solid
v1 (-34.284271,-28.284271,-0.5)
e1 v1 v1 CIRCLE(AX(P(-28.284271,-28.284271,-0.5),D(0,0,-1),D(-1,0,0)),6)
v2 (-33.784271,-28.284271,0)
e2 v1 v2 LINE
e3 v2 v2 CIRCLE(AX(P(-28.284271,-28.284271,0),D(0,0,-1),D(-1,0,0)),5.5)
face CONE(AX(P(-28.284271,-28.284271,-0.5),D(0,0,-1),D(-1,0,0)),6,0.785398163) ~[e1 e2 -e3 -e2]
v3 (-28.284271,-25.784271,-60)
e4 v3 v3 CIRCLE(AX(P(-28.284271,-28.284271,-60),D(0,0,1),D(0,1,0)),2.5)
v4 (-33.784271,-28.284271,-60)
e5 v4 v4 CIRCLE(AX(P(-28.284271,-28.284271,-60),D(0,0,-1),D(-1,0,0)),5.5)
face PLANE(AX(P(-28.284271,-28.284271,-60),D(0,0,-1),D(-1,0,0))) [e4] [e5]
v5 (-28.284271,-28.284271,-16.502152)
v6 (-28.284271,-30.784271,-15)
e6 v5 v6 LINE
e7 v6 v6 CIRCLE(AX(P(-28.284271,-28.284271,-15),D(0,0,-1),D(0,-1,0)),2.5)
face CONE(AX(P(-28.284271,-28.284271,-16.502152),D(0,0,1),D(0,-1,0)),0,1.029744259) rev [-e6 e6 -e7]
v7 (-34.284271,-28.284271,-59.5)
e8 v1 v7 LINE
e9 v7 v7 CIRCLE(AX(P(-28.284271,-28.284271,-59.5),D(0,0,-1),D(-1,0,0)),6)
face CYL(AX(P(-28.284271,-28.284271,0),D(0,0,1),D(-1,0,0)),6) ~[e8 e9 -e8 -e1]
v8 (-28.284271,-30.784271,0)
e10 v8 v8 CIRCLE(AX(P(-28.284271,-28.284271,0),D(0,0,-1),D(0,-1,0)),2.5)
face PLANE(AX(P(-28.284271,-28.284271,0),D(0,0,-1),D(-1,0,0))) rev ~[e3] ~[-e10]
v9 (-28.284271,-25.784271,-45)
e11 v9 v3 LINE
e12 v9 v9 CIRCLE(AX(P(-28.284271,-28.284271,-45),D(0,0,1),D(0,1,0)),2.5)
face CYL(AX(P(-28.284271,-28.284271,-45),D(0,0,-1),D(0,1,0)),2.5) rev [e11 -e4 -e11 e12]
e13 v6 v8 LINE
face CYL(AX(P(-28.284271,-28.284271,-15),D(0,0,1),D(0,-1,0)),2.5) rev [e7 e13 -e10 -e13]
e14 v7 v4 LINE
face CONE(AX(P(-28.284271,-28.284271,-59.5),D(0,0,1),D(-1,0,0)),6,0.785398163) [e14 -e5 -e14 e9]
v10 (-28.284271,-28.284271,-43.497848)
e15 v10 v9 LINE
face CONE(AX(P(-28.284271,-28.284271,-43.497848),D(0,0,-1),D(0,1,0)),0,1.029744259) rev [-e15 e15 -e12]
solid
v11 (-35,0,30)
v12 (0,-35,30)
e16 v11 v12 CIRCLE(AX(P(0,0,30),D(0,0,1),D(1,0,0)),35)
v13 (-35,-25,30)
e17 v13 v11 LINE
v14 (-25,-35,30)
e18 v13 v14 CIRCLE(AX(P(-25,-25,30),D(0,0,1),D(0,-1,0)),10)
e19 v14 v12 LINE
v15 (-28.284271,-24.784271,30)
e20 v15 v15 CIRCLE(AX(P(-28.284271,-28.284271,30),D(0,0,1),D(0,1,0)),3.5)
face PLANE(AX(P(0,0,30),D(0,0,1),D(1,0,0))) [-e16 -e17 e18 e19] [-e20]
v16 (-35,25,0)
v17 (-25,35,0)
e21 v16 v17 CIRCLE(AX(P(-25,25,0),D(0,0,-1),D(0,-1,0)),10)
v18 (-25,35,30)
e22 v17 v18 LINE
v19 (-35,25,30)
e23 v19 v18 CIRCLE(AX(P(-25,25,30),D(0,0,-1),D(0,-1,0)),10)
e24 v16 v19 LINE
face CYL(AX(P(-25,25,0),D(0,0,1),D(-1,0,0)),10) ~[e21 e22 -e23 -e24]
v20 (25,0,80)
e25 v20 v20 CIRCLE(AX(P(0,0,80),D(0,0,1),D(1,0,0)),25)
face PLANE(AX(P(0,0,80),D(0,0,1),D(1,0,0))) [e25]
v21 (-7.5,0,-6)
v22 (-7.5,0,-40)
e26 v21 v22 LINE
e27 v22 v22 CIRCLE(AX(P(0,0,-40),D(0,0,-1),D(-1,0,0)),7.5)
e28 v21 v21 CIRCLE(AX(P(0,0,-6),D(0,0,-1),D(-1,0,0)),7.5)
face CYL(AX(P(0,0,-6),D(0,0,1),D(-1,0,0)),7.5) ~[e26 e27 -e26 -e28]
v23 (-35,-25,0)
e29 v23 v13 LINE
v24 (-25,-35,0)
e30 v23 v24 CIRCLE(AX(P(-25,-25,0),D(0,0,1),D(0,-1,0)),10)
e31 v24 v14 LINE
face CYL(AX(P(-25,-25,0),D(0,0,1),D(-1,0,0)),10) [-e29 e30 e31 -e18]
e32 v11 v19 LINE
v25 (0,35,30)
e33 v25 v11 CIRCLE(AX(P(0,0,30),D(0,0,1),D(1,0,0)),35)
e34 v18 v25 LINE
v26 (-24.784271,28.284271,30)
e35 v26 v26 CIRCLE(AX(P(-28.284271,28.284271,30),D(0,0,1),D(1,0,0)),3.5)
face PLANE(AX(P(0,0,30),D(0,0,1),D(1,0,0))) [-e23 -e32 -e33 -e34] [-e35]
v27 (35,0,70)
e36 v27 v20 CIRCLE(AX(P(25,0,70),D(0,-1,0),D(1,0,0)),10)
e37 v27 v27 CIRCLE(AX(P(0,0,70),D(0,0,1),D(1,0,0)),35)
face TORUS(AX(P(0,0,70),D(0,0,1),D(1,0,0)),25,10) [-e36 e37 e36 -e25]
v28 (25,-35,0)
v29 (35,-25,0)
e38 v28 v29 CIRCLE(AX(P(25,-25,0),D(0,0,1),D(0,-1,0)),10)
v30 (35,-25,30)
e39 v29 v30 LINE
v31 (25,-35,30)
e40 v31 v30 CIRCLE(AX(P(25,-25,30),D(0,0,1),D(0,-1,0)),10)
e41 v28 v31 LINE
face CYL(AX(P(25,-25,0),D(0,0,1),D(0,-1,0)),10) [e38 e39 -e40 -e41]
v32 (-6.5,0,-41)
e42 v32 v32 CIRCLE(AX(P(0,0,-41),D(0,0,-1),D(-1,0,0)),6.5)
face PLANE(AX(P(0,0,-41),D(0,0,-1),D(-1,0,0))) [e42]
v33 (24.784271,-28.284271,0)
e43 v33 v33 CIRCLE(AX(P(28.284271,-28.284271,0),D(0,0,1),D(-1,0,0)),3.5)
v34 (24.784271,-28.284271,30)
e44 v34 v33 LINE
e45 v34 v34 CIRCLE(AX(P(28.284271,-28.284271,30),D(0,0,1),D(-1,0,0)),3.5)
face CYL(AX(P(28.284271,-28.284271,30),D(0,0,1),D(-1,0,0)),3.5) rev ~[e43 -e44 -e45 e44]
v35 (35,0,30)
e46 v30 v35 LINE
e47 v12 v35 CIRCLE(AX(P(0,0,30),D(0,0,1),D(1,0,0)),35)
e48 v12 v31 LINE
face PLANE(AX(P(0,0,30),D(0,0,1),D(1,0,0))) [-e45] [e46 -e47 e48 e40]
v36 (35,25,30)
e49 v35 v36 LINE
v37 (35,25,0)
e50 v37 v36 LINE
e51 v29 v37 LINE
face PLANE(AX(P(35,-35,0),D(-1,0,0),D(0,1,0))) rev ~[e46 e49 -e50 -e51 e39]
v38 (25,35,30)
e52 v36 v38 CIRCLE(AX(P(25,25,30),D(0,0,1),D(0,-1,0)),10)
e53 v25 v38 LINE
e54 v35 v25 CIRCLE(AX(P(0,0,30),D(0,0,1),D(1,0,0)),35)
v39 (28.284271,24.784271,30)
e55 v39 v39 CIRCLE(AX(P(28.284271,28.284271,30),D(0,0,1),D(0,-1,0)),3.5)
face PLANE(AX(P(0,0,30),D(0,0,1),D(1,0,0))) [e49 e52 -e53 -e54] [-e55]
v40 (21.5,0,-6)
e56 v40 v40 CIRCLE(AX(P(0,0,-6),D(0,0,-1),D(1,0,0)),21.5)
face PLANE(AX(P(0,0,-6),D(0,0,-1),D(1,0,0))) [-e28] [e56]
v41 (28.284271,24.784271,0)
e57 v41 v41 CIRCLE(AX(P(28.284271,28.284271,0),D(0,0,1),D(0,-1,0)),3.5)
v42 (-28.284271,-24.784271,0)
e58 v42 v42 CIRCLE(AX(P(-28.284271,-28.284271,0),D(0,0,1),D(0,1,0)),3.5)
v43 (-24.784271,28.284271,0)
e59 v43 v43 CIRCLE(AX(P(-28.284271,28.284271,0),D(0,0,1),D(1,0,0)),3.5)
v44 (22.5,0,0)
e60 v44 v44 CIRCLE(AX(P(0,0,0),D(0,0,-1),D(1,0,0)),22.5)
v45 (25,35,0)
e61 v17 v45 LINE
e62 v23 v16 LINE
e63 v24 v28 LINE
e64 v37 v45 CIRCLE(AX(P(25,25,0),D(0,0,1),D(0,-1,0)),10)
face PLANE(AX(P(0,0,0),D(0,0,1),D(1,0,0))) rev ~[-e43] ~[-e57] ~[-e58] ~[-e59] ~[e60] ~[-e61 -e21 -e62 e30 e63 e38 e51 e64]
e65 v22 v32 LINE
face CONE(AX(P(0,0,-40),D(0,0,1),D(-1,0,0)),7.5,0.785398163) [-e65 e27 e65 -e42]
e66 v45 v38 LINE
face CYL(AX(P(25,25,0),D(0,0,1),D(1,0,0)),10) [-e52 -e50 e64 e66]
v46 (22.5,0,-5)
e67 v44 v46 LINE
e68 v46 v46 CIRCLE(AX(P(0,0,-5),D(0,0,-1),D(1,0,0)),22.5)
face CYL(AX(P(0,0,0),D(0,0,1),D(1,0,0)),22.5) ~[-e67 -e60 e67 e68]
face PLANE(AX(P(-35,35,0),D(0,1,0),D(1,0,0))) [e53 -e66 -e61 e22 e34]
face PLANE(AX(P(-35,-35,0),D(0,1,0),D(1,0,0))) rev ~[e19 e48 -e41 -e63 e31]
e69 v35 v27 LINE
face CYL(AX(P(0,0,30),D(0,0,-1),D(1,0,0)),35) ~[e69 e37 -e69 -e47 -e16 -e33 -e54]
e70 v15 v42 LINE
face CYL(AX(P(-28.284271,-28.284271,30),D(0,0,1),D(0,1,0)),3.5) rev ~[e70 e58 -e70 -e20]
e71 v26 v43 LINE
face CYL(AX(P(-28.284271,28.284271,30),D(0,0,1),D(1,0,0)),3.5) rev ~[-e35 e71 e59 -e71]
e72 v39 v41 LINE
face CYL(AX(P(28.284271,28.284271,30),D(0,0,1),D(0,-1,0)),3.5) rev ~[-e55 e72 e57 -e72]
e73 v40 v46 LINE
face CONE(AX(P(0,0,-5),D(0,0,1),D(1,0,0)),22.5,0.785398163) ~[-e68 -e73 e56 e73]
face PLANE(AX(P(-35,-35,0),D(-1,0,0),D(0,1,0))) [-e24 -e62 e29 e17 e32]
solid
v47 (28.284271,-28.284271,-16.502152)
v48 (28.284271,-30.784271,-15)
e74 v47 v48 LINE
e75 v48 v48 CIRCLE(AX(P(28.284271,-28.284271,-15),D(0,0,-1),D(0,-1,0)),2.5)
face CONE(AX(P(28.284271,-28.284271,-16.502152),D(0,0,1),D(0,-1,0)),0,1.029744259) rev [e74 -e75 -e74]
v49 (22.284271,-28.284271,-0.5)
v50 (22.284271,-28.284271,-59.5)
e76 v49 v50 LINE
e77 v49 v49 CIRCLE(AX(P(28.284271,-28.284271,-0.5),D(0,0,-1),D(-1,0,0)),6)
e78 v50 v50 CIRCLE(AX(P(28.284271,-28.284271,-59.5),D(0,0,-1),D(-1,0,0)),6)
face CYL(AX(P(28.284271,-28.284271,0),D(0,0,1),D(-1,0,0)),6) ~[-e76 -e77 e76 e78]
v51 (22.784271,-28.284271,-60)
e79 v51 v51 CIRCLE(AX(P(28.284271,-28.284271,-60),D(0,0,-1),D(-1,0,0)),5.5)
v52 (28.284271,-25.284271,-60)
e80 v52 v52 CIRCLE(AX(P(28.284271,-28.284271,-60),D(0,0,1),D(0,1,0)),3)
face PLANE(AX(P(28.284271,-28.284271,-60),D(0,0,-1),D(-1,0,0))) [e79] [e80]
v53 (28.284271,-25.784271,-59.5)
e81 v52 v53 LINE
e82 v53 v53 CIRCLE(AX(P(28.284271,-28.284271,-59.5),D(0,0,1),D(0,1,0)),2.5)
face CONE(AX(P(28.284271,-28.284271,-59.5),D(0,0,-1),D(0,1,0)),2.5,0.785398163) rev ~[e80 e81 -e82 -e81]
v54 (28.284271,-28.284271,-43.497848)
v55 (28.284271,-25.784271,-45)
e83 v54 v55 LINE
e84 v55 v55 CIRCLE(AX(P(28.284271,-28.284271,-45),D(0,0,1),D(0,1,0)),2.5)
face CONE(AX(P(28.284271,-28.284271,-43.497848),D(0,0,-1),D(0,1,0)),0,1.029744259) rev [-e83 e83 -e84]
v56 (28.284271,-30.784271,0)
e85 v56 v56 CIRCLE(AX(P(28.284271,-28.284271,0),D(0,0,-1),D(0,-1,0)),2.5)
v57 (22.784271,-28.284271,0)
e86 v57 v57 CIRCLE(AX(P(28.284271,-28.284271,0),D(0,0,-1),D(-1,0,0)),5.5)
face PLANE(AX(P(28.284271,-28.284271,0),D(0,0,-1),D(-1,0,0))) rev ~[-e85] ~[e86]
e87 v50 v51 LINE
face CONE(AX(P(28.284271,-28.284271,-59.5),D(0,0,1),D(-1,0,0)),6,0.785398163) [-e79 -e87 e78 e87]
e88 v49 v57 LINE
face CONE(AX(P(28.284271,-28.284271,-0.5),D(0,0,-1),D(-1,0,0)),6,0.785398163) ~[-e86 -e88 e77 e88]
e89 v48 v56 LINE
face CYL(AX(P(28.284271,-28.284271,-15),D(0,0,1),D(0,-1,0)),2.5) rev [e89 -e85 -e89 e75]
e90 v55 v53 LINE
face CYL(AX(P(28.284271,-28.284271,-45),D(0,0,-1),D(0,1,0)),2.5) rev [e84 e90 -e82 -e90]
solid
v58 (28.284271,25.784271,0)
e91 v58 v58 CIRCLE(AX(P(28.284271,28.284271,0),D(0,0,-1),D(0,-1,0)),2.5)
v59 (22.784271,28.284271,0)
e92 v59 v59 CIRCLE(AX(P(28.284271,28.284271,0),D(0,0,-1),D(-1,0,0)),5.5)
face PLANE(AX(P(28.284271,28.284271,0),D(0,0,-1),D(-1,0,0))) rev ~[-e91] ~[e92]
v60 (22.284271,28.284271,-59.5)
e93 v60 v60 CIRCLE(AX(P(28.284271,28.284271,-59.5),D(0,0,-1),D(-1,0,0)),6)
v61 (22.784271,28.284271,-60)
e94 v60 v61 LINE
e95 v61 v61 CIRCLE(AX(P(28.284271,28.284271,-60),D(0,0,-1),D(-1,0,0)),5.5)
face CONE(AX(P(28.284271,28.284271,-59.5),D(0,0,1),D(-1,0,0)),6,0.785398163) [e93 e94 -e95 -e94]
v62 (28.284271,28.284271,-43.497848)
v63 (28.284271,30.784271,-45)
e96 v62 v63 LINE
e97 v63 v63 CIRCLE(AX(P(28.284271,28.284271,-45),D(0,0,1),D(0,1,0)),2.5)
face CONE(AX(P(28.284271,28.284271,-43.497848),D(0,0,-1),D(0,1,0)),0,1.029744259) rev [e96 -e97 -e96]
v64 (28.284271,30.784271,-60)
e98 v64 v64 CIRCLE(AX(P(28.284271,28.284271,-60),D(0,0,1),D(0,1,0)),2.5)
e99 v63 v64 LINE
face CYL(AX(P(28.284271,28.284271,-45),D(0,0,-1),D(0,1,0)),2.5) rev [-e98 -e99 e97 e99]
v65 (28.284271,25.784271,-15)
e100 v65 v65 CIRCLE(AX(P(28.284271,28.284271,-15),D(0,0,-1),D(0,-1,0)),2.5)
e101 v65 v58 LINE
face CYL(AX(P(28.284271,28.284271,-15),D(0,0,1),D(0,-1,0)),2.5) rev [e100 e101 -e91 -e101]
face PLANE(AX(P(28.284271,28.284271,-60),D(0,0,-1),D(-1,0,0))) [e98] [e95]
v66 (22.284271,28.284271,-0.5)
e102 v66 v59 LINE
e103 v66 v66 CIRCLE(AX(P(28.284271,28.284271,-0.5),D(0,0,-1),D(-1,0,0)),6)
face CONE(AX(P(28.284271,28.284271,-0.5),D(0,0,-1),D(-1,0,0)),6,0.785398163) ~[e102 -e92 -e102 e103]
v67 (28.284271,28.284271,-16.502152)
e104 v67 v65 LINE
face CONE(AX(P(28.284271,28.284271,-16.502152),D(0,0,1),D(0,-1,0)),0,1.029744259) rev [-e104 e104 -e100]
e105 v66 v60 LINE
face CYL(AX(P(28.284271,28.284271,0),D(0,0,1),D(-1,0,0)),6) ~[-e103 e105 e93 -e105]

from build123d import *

# Parameters (mm, degrees)
SKETCH1_W                  = 70
SKETCH1_H                  = 70
BOSS_EXTRUDE1_DEPTH        = 30
FILLET2_R                  = 10
SKETCH3_R                  = 3.5
CUT_EXTRUDE1_DEPTH         = 60
SKETCH4_R                  = 22.5
BOSS_EXTRUDE3_DEPTH        = 6
SKETCH5_R                  = 7.5
BOSS_EXTRUDE4_DEPTH        = 35
CHAMFER1_SIZE              = 1
CHAMFER2_SIZE              = 1
CIRPATTERN1_COUNT          = 4
SKETCH6_R                  = 35
BOSS_EXTRUDE5_DEPTH        = 50
FILLET3_R                  = 10
SKETCH7_R                  = 6
BOSS_EXTRUDE6_DEPTH        = 60
BOSS_EXTRUDE6_2_DEPTH      = 60
BOSS_EXTRUDE6_3_DEPTH      = 60
M6_TAPPED_HOLE1_AT_2_COUNT = 2
M6_TAPPED_HOLE1_AT_2_PITCH = 80
M6_TAPPED_HOLE1_AT_3_COUNT = 2
M6_TAPPED_HOLE1_AT_3_PITCH = 56.568542495
CHAMFER3_SIZE              = 0.5
CHAMFER5_SIZE              = 0.5
CHAMFER6_SIZE              = 0.5
M6_TAPPED_HOLE2_AT_2_COUNT = 2
M6_TAPPED_HOLE2_AT_2_PITCH = 80
M6_TAPPED_HOLE2_AT_3_COUNT = 2
M6_TAPPED_HOLE2_AT_3_PITCH = 56.568542495


with BuildPart() as part:
    # Sketch1 → Boss-Extrude1 (new body)
    with BuildSketch(Plane.XY):
        Rectangle(SKETCH1_W, SKETCH1_H)
    extrude(amount=BOSS_EXTRUDE1_DEPTH)

    # Fillet2
    fillet2_edges = [part.edges().sort_by_distance(p)[0] for p in [
        (-35, 35, 15),
        (35, 35, 15),
        (35, -35, 15),
        (-35, -35, 15),
    ]]
    fillet(fillet2_edges, radius=FILLET2_R)

    # Sketch3 → Cut-Extrude1 (cut)
    with BuildSketch(Plane.XY.offset(30)):
        with Locations((-28.284271247, 28.284271247)):
            Circle(SKETCH3_R)
    cut_extrude1 = extrude(amount=-CUT_EXTRUDE1_DEPTH, mode=Mode.SUBTRACT)

    # Sketch4 → Boss-Extrude3 (add)
    with BuildSketch(Plane(origin=(0, 0, 0), x_dir=(-1, 0, 0), z_dir=(0, 0, -1))):
        with Locations(Location((0, 0, 0), (0, 0, 180))):
            Circle(SKETCH4_R)
    extrude(amount=BOSS_EXTRUDE3_DEPTH)

    # Sketch5 → Boss-Extrude4 (add)
    with BuildSketch(Plane(origin=(0, 0, -6), x_dir=(-1, 0, 0), z_dir=(0, 0, -1))):
        Circle(SKETCH5_R)
    extrude(amount=BOSS_EXTRUDE4_DEPTH)

    # Chamfer1
    chamfer1_edges = [part.edges().sort_by_distance(p)[0] for p in [
        (7.5, 0, -41),
    ]]
    chamfer(chamfer1_edges, length=CHAMFER1_SIZE)

    # Chamfer2
    chamfer2_edges = [part.edges().sort_by_distance(p)[0] for p in [
        (-22.5, 0, -6),
    ]]
    chamfer(chamfer2_edges, length=CHAMFER2_SIZE)

    # CirPattern1: Cut-Extrude1 ×4 about axis
    cirpattern1_axis = Axis((0, 0, 0), (0, 0, 1))
    for i in range(1, CIRPATTERN1_COUNT):
        add(cut_extrude1.rotate(cirpattern1_axis, i * 360 / CIRPATTERN1_COUNT), mode=Mode.SUBTRACT)

    # Sketch6 → Boss-Extrude5 (add)
    with BuildSketch(Plane.XY.offset(30)):
        Circle(SKETCH6_R)
    extrude(amount=BOSS_EXTRUDE5_DEPTH)

    # Fillet3
    fillet3_edges = [part.edges().sort_by_distance(p)[0] for p in [
        (-35, 0, 80),
    ]]
    fillet(fillet3_edges, radius=FILLET3_R)


with BuildPart() as body_2:
    # Sketch7 → Boss-Extrude6 (new body)
    with BuildSketch(Plane(origin=(0, 0, 0), x_dir=(-1, 0, 0), z_dir=(0, 0, -1))):
        with Locations((-28.284271247, 28.284271247)):
            Circle(SKETCH7_R)
    extrude(amount=BOSS_EXTRUDE6_DEPTH)

    # Sketch9 → M6 Tapped Hole1 (revolve, cut)
    with BuildSketch(Plane(origin=(28.284271247, 28.284271247, -60), x_dir=(0, 1, 0), z_dir=(1, 0, 0))):
        Polygon((0, 0), (0, 16.502151548), (2.5, 15), (2.5, 0), align=None)
    m6_tapped_hole1 = revolve(axis=Axis((28.284271247, 28.284271247, -66.35), (0, 0, 1)), mode=Mode.SUBTRACT)

    # Chamfer3
    chamfer3_edges = [body_2.edges().sort_by_distance(p)[0] for p in [
        (34.284271247, 28.284271247, 0),
        (34.284271247, 28.284271247, -60),
    ]]
    chamfer(chamfer3_edges, length=CHAMFER3_SIZE)

    # Sketch11 → M6 Tapped Hole2 (revolve, cut)
    with BuildSketch(Plane(origin=(28.284271247, 28.284271247, 0), x_dir=(0, -1, 0), z_dir=(1, 0, 0))):
        Polygon((0, 0), (0, 16.502151548), (2.5, 15), (2.5, 0), align=None)
    m6_tapped_hole2 = revolve(axis=Axis((28.284271247, 28.284271247, 6.35), (0, 0, -1)), mode=Mode.SUBTRACT)


with BuildPart() as body_3:
    # Sketch7 → Boss-Extrude6 2 (new body)
    with BuildSketch(Plane(origin=(0, 0, 0), x_dir=(-1, 0, 0), z_dir=(0, 0, -1))):
        with Locations((28.284271247, -28.284271247)):
            Circle(SKETCH7_R)
    extrude(amount=BOSS_EXTRUDE6_2_DEPTH)

    # M6 Tapped Hole1 at 2: M6 Tapped Hole1 ×2
    with Locations(*[Vector(-0.7071067811865429, -0.7071067811865522, 0) * (i * M6_TAPPED_HOLE1_AT_2_PITCH) for i in range(1, M6_TAPPED_HOLE1_AT_2_COUNT)]):
        add(m6_tapped_hole1, mode=Mode.SUBTRACT)

    # Chamfer6
    chamfer6_edges = [body_3.edges().sort_by_distance(p)[0] for p in [
        (-22.284271247, -28.284271247, 0),
        (-22.284271247, -28.284271247, -60),
    ]]
    chamfer(chamfer6_edges, length=CHAMFER6_SIZE)

    # M6 Tapped Hole2 at 2: M6 Tapped Hole2 ×2
    with Locations(*[Vector(-0.7071067811865429, -0.7071067811865522, 0) * (i * M6_TAPPED_HOLE2_AT_2_PITCH) for i in range(1, M6_TAPPED_HOLE2_AT_2_COUNT)]):
        add(m6_tapped_hole2, mode=Mode.SUBTRACT)


with BuildPart() as body_4:
    # Sketch7 → Boss-Extrude6 3 (new body)
    with BuildSketch(Plane(origin=(0, 0, 0), x_dir=(-1, 0, 0), z_dir=(0, 0, -1))):
        with Locations((-28.284271247, -28.284271247)):
            Circle(SKETCH7_R)
    extrude(amount=BOSS_EXTRUDE6_3_DEPTH)

    # M6 Tapped Hole1 at 3: M6 Tapped Hole1 ×2
    with Locations(*[(0, -i * M6_TAPPED_HOLE1_AT_3_PITCH, 0) for i in range(1, M6_TAPPED_HOLE1_AT_3_COUNT)]):
        add(m6_tapped_hole1, mode=Mode.SUBTRACT)

    # Chamfer5
    chamfer5_edges = [body_4.edges().sort_by_distance(p)[0] for p in [
        (34.284271247, -28.284271247, 0),
        (34.284271247, -28.284271247, -60),
        (28.284271247, -30.784271247, -60),
    ]]
    chamfer(chamfer5_edges, length=CHAMFER5_SIZE)

    # M6 Tapped Hole2 at 3: M6 Tapped Hole2 ×2
    with Locations(*[(0, -i * M6_TAPPED_HOLE2_AT_3_PITCH, 0) for i in range(1, M6_TAPPED_HOLE2_AT_3_COUNT)]):
        add(m6_tapped_hole2, mode=Mode.SUBTRACT)


solid = Compound([part.part, body_2.part, body_3.part, body_4.part])
